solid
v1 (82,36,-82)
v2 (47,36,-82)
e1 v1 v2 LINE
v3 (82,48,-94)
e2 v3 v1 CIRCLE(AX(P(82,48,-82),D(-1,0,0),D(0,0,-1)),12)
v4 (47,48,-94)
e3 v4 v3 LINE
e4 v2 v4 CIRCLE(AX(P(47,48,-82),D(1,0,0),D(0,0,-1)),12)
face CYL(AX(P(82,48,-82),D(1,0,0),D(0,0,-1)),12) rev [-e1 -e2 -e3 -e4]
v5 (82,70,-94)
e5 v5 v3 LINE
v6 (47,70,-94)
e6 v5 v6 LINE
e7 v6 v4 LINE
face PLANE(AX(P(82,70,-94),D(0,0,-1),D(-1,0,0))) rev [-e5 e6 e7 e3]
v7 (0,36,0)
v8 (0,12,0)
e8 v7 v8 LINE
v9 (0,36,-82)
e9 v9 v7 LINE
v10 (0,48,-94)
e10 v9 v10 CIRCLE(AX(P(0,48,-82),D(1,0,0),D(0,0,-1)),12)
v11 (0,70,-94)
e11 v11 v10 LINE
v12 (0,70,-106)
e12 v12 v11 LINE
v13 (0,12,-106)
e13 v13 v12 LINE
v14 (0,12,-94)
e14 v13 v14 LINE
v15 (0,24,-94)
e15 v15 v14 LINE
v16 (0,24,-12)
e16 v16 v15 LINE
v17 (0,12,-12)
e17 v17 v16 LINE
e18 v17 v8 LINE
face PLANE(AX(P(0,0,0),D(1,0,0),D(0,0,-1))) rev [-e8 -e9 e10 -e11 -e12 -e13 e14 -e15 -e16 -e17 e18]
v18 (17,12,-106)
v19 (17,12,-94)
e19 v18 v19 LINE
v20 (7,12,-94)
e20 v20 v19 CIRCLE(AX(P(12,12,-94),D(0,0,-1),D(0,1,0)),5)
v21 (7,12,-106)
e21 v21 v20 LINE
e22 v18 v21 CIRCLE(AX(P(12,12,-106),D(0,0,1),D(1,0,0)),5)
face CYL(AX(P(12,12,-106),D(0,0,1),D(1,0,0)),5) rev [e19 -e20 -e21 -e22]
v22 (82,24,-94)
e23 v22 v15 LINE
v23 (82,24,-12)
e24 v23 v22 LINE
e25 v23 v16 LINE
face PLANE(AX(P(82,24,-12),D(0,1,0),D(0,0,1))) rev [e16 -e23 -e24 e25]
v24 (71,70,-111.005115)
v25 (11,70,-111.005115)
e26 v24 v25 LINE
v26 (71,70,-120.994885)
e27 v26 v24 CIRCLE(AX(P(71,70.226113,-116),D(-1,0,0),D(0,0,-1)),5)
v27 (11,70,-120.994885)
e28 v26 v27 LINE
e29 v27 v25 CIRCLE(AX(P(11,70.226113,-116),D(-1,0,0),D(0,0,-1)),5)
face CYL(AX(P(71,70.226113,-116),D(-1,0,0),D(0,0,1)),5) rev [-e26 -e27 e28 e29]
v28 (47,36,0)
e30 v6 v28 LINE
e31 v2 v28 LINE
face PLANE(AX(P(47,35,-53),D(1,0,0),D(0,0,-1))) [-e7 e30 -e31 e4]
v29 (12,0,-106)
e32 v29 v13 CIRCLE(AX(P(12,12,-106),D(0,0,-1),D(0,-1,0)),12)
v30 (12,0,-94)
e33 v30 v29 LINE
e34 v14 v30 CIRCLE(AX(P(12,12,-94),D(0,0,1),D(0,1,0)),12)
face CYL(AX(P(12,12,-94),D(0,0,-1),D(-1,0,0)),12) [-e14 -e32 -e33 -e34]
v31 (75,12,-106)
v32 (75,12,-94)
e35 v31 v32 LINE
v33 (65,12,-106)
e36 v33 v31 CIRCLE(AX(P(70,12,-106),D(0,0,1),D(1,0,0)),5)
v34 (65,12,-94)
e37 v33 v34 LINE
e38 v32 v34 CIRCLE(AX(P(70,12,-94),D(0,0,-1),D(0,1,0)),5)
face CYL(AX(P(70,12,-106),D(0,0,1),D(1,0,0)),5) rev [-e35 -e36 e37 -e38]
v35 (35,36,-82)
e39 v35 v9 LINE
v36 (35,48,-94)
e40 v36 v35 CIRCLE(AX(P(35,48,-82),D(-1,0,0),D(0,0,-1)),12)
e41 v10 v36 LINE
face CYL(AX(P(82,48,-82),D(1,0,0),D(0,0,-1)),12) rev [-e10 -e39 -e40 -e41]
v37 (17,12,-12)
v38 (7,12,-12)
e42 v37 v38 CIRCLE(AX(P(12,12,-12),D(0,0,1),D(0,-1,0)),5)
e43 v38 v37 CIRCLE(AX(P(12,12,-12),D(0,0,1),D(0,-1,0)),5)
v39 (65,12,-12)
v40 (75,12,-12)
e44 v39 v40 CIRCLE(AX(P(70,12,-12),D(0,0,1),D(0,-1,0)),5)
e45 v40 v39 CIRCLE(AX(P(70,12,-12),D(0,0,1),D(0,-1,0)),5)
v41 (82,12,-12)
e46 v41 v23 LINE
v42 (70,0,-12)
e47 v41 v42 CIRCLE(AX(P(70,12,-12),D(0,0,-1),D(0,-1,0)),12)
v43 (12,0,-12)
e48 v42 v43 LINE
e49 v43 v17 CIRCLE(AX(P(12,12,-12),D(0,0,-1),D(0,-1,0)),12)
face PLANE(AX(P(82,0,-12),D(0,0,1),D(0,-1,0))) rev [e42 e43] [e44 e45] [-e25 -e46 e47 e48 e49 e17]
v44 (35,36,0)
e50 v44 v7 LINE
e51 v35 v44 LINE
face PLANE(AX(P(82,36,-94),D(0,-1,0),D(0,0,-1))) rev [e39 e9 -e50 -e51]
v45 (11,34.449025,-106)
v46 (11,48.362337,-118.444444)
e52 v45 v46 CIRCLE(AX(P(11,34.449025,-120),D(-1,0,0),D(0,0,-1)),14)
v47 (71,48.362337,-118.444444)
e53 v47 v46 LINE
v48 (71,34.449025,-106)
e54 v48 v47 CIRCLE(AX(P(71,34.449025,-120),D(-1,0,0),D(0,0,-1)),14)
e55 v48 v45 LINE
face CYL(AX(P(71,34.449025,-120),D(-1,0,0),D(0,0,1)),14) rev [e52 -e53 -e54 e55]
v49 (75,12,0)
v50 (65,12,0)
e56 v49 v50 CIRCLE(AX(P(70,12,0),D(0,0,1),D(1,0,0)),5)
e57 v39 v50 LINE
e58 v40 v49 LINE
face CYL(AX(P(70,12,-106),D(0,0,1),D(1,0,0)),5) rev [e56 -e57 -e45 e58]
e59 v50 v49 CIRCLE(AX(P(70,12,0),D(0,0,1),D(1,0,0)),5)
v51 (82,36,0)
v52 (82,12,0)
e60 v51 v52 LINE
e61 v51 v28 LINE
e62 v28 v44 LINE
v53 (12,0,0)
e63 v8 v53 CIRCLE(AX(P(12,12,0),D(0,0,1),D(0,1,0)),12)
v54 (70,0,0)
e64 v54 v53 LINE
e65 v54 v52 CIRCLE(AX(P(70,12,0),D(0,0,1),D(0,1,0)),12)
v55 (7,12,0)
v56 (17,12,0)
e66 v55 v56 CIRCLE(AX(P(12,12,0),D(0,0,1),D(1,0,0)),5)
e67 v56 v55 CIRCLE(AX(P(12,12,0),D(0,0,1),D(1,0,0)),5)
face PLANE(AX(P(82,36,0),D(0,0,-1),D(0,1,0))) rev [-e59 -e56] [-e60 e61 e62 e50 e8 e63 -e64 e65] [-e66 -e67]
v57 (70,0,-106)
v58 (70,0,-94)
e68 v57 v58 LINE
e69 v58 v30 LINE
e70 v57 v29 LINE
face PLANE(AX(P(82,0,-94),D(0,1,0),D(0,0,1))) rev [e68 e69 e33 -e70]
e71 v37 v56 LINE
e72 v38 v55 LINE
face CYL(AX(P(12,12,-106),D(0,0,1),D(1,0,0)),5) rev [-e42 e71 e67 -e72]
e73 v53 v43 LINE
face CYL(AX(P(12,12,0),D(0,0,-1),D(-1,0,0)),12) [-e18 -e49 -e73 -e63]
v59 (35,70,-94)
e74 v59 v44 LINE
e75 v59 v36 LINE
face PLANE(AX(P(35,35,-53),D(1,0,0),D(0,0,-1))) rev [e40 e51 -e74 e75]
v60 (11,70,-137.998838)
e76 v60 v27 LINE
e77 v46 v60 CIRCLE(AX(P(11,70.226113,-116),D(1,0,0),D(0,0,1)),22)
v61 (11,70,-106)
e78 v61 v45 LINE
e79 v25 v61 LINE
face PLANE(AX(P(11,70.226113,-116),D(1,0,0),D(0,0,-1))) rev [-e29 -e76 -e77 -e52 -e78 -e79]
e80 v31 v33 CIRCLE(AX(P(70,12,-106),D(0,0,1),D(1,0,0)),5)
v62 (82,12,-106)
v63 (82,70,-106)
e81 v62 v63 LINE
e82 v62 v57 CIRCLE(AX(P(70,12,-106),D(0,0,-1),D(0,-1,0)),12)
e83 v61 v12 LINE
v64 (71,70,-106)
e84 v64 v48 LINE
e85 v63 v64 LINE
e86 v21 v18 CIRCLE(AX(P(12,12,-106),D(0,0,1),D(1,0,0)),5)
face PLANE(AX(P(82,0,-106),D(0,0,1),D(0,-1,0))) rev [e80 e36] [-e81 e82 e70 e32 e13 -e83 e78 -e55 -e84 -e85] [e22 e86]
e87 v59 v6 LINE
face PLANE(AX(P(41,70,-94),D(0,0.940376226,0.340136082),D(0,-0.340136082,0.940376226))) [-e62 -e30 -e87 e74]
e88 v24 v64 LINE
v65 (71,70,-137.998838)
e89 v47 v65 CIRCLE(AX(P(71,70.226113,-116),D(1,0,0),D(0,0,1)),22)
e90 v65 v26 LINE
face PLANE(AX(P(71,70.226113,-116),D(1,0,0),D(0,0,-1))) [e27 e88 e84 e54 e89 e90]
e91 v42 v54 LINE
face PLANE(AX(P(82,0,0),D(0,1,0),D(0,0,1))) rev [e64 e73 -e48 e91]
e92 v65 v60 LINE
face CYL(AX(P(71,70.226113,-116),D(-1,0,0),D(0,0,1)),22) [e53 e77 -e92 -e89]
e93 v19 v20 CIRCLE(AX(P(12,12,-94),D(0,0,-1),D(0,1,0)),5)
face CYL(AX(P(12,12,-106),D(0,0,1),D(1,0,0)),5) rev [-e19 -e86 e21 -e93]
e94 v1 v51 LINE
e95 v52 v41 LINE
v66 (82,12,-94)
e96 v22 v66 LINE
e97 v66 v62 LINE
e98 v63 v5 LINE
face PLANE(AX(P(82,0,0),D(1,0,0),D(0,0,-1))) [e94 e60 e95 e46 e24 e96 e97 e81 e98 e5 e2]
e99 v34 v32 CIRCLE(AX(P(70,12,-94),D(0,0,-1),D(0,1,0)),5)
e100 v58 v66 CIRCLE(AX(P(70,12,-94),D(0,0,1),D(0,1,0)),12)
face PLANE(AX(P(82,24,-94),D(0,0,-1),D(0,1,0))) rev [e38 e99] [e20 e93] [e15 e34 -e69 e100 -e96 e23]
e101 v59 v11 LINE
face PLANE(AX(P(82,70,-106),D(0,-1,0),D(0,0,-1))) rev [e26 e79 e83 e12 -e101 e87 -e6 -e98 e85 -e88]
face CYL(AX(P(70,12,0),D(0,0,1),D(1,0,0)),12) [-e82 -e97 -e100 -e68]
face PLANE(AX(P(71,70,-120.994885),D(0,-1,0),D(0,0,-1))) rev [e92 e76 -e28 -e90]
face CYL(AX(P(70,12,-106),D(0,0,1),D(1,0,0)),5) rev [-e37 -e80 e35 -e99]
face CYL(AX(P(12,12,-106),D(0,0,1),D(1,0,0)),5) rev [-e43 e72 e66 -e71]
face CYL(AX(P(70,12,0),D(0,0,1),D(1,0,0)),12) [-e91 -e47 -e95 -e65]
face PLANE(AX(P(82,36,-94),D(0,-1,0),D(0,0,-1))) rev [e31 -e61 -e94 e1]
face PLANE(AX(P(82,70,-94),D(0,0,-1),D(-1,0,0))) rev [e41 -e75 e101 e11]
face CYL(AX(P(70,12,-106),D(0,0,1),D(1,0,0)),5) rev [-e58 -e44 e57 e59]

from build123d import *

# Parameters (mm, degrees)
BRACKET_BODY_DEPTH        = 82
BODY_CORNER_FILLETS_R12_R = 12
MOUNTING_HOLES_SKETCH_R   = 5
MOUNTING_HOLES_DEPTH      = 152.19523802
CENTRE_RIB_12MM_REACH     = 135.48
RIB_SKETCH_WALL_W         = 368.920663258
RIB_SKETCH_WALL_H         = 12
INNER_CORNER_FILLET_R12_R = 12
CRADLE_BOSS_DEPTH         = 30


with BuildPart() as part:
    # Bracket Profile Sketch → Bracket Body (new body)
    with BuildSketch(Plane(origin=(0, 0, 0), x_dir=(0, 0, -1), z_dir=(1, 0, 0))):
        Polygon((0, 0), (12, 0), (12, 24), (94, 24), (94, 0), (106, 0), (106, 70), (94, 70), (94, 36), (0, 36), align=None)
    extrude(amount=BRACKET_BODY_DEPTH)

    # Body Corner Fillets R12
    body_corner_fillets_r12_edges = [part.edges().sort_by_distance(p)[0] for p in [
        (0, 0, -100),
        (0, 0, -6),
        (82, 0, -100),
        (82, 0, -6),
    ]]
    fillet(body_corner_fillets_r12_edges, radius=BODY_CORNER_FILLETS_R12_R)

    # Mounting Holes Sketch → Mounting Holes (cut, through all)
    with BuildSketch(Plane.XY):
        with Locations((12, 12)):
            Circle(MOUNTING_HOLES_SKETCH_R)
        with Locations((70, 12)):
            Circle(MOUNTING_HOLES_SKETCH_R)
    extrude(amount=-MOUNTING_HOLES_DEPTH, mode=Mode.SUBTRACT)

    # Rib Sketch wall → Centre Rib 12mm (add, up to next)
    with BuildSketch(Plane(origin=(41, 53, -47), x_dir=(0, -0.340136081654, 0.940376225751), z_dir=(0, -0.940376225751, -0.340136081654)), mode=Mode.PRIVATE) as centre_rib_12mm_sk1:
        Rectangle(RIB_SKETCH_WALL_W, RIB_SKETCH_WALL_H)
    centre_rib_12mm_tool1 = extrude(centre_rib_12mm_sk1.sketch, amount=CENTRE_RIB_12MM_REACH, mode=Mode.PRIVATE) - part.part
    add(centre_rib_12mm_tool1.solids().sort_by_distance((41, 53, -47))[0])

    # Inner Corner Fillet R12
    inner_corner_fillet_r12_edges = [part.edges().sort_by_distance(p)[0] for p in [
        (64.5, 36, -94),
        (17.5, 36, -94),
    ]]
    fillet(inner_corner_fillet_r12_edges, radius=INNER_CORNER_FILLET_R12_R)

    # Cradle Profile Sketch → Cradle Boss (add, symmetric)
    with BuildSketch(Plane(origin=(41, 0, 0), x_dir=(0, 0, -1), z_dir=(1, 0, 0))):
        with BuildLine():
            Line((120.994884686, 70), (137.998837993, 70))
            ThreePointArc((137.998837993, 70), (132.322243398, 55.475371387), (118.444444444, 48.362336959))
            ThreePointArc((118.444444444, 48.362336959), (109.565016105, 43.782358433), (106, 34.449025099))
            Line((106, 34.449025099), (106, 70))
            Line((106, 70), (111.005115314, 70))
            ThreePointArc((111.005115314, 70), (116, 65.226112739), (120.994884686, 70))
        make_face()
    extrude(amount=CRADLE_BOSS_DEPTH, both=True)


solid = part.part
